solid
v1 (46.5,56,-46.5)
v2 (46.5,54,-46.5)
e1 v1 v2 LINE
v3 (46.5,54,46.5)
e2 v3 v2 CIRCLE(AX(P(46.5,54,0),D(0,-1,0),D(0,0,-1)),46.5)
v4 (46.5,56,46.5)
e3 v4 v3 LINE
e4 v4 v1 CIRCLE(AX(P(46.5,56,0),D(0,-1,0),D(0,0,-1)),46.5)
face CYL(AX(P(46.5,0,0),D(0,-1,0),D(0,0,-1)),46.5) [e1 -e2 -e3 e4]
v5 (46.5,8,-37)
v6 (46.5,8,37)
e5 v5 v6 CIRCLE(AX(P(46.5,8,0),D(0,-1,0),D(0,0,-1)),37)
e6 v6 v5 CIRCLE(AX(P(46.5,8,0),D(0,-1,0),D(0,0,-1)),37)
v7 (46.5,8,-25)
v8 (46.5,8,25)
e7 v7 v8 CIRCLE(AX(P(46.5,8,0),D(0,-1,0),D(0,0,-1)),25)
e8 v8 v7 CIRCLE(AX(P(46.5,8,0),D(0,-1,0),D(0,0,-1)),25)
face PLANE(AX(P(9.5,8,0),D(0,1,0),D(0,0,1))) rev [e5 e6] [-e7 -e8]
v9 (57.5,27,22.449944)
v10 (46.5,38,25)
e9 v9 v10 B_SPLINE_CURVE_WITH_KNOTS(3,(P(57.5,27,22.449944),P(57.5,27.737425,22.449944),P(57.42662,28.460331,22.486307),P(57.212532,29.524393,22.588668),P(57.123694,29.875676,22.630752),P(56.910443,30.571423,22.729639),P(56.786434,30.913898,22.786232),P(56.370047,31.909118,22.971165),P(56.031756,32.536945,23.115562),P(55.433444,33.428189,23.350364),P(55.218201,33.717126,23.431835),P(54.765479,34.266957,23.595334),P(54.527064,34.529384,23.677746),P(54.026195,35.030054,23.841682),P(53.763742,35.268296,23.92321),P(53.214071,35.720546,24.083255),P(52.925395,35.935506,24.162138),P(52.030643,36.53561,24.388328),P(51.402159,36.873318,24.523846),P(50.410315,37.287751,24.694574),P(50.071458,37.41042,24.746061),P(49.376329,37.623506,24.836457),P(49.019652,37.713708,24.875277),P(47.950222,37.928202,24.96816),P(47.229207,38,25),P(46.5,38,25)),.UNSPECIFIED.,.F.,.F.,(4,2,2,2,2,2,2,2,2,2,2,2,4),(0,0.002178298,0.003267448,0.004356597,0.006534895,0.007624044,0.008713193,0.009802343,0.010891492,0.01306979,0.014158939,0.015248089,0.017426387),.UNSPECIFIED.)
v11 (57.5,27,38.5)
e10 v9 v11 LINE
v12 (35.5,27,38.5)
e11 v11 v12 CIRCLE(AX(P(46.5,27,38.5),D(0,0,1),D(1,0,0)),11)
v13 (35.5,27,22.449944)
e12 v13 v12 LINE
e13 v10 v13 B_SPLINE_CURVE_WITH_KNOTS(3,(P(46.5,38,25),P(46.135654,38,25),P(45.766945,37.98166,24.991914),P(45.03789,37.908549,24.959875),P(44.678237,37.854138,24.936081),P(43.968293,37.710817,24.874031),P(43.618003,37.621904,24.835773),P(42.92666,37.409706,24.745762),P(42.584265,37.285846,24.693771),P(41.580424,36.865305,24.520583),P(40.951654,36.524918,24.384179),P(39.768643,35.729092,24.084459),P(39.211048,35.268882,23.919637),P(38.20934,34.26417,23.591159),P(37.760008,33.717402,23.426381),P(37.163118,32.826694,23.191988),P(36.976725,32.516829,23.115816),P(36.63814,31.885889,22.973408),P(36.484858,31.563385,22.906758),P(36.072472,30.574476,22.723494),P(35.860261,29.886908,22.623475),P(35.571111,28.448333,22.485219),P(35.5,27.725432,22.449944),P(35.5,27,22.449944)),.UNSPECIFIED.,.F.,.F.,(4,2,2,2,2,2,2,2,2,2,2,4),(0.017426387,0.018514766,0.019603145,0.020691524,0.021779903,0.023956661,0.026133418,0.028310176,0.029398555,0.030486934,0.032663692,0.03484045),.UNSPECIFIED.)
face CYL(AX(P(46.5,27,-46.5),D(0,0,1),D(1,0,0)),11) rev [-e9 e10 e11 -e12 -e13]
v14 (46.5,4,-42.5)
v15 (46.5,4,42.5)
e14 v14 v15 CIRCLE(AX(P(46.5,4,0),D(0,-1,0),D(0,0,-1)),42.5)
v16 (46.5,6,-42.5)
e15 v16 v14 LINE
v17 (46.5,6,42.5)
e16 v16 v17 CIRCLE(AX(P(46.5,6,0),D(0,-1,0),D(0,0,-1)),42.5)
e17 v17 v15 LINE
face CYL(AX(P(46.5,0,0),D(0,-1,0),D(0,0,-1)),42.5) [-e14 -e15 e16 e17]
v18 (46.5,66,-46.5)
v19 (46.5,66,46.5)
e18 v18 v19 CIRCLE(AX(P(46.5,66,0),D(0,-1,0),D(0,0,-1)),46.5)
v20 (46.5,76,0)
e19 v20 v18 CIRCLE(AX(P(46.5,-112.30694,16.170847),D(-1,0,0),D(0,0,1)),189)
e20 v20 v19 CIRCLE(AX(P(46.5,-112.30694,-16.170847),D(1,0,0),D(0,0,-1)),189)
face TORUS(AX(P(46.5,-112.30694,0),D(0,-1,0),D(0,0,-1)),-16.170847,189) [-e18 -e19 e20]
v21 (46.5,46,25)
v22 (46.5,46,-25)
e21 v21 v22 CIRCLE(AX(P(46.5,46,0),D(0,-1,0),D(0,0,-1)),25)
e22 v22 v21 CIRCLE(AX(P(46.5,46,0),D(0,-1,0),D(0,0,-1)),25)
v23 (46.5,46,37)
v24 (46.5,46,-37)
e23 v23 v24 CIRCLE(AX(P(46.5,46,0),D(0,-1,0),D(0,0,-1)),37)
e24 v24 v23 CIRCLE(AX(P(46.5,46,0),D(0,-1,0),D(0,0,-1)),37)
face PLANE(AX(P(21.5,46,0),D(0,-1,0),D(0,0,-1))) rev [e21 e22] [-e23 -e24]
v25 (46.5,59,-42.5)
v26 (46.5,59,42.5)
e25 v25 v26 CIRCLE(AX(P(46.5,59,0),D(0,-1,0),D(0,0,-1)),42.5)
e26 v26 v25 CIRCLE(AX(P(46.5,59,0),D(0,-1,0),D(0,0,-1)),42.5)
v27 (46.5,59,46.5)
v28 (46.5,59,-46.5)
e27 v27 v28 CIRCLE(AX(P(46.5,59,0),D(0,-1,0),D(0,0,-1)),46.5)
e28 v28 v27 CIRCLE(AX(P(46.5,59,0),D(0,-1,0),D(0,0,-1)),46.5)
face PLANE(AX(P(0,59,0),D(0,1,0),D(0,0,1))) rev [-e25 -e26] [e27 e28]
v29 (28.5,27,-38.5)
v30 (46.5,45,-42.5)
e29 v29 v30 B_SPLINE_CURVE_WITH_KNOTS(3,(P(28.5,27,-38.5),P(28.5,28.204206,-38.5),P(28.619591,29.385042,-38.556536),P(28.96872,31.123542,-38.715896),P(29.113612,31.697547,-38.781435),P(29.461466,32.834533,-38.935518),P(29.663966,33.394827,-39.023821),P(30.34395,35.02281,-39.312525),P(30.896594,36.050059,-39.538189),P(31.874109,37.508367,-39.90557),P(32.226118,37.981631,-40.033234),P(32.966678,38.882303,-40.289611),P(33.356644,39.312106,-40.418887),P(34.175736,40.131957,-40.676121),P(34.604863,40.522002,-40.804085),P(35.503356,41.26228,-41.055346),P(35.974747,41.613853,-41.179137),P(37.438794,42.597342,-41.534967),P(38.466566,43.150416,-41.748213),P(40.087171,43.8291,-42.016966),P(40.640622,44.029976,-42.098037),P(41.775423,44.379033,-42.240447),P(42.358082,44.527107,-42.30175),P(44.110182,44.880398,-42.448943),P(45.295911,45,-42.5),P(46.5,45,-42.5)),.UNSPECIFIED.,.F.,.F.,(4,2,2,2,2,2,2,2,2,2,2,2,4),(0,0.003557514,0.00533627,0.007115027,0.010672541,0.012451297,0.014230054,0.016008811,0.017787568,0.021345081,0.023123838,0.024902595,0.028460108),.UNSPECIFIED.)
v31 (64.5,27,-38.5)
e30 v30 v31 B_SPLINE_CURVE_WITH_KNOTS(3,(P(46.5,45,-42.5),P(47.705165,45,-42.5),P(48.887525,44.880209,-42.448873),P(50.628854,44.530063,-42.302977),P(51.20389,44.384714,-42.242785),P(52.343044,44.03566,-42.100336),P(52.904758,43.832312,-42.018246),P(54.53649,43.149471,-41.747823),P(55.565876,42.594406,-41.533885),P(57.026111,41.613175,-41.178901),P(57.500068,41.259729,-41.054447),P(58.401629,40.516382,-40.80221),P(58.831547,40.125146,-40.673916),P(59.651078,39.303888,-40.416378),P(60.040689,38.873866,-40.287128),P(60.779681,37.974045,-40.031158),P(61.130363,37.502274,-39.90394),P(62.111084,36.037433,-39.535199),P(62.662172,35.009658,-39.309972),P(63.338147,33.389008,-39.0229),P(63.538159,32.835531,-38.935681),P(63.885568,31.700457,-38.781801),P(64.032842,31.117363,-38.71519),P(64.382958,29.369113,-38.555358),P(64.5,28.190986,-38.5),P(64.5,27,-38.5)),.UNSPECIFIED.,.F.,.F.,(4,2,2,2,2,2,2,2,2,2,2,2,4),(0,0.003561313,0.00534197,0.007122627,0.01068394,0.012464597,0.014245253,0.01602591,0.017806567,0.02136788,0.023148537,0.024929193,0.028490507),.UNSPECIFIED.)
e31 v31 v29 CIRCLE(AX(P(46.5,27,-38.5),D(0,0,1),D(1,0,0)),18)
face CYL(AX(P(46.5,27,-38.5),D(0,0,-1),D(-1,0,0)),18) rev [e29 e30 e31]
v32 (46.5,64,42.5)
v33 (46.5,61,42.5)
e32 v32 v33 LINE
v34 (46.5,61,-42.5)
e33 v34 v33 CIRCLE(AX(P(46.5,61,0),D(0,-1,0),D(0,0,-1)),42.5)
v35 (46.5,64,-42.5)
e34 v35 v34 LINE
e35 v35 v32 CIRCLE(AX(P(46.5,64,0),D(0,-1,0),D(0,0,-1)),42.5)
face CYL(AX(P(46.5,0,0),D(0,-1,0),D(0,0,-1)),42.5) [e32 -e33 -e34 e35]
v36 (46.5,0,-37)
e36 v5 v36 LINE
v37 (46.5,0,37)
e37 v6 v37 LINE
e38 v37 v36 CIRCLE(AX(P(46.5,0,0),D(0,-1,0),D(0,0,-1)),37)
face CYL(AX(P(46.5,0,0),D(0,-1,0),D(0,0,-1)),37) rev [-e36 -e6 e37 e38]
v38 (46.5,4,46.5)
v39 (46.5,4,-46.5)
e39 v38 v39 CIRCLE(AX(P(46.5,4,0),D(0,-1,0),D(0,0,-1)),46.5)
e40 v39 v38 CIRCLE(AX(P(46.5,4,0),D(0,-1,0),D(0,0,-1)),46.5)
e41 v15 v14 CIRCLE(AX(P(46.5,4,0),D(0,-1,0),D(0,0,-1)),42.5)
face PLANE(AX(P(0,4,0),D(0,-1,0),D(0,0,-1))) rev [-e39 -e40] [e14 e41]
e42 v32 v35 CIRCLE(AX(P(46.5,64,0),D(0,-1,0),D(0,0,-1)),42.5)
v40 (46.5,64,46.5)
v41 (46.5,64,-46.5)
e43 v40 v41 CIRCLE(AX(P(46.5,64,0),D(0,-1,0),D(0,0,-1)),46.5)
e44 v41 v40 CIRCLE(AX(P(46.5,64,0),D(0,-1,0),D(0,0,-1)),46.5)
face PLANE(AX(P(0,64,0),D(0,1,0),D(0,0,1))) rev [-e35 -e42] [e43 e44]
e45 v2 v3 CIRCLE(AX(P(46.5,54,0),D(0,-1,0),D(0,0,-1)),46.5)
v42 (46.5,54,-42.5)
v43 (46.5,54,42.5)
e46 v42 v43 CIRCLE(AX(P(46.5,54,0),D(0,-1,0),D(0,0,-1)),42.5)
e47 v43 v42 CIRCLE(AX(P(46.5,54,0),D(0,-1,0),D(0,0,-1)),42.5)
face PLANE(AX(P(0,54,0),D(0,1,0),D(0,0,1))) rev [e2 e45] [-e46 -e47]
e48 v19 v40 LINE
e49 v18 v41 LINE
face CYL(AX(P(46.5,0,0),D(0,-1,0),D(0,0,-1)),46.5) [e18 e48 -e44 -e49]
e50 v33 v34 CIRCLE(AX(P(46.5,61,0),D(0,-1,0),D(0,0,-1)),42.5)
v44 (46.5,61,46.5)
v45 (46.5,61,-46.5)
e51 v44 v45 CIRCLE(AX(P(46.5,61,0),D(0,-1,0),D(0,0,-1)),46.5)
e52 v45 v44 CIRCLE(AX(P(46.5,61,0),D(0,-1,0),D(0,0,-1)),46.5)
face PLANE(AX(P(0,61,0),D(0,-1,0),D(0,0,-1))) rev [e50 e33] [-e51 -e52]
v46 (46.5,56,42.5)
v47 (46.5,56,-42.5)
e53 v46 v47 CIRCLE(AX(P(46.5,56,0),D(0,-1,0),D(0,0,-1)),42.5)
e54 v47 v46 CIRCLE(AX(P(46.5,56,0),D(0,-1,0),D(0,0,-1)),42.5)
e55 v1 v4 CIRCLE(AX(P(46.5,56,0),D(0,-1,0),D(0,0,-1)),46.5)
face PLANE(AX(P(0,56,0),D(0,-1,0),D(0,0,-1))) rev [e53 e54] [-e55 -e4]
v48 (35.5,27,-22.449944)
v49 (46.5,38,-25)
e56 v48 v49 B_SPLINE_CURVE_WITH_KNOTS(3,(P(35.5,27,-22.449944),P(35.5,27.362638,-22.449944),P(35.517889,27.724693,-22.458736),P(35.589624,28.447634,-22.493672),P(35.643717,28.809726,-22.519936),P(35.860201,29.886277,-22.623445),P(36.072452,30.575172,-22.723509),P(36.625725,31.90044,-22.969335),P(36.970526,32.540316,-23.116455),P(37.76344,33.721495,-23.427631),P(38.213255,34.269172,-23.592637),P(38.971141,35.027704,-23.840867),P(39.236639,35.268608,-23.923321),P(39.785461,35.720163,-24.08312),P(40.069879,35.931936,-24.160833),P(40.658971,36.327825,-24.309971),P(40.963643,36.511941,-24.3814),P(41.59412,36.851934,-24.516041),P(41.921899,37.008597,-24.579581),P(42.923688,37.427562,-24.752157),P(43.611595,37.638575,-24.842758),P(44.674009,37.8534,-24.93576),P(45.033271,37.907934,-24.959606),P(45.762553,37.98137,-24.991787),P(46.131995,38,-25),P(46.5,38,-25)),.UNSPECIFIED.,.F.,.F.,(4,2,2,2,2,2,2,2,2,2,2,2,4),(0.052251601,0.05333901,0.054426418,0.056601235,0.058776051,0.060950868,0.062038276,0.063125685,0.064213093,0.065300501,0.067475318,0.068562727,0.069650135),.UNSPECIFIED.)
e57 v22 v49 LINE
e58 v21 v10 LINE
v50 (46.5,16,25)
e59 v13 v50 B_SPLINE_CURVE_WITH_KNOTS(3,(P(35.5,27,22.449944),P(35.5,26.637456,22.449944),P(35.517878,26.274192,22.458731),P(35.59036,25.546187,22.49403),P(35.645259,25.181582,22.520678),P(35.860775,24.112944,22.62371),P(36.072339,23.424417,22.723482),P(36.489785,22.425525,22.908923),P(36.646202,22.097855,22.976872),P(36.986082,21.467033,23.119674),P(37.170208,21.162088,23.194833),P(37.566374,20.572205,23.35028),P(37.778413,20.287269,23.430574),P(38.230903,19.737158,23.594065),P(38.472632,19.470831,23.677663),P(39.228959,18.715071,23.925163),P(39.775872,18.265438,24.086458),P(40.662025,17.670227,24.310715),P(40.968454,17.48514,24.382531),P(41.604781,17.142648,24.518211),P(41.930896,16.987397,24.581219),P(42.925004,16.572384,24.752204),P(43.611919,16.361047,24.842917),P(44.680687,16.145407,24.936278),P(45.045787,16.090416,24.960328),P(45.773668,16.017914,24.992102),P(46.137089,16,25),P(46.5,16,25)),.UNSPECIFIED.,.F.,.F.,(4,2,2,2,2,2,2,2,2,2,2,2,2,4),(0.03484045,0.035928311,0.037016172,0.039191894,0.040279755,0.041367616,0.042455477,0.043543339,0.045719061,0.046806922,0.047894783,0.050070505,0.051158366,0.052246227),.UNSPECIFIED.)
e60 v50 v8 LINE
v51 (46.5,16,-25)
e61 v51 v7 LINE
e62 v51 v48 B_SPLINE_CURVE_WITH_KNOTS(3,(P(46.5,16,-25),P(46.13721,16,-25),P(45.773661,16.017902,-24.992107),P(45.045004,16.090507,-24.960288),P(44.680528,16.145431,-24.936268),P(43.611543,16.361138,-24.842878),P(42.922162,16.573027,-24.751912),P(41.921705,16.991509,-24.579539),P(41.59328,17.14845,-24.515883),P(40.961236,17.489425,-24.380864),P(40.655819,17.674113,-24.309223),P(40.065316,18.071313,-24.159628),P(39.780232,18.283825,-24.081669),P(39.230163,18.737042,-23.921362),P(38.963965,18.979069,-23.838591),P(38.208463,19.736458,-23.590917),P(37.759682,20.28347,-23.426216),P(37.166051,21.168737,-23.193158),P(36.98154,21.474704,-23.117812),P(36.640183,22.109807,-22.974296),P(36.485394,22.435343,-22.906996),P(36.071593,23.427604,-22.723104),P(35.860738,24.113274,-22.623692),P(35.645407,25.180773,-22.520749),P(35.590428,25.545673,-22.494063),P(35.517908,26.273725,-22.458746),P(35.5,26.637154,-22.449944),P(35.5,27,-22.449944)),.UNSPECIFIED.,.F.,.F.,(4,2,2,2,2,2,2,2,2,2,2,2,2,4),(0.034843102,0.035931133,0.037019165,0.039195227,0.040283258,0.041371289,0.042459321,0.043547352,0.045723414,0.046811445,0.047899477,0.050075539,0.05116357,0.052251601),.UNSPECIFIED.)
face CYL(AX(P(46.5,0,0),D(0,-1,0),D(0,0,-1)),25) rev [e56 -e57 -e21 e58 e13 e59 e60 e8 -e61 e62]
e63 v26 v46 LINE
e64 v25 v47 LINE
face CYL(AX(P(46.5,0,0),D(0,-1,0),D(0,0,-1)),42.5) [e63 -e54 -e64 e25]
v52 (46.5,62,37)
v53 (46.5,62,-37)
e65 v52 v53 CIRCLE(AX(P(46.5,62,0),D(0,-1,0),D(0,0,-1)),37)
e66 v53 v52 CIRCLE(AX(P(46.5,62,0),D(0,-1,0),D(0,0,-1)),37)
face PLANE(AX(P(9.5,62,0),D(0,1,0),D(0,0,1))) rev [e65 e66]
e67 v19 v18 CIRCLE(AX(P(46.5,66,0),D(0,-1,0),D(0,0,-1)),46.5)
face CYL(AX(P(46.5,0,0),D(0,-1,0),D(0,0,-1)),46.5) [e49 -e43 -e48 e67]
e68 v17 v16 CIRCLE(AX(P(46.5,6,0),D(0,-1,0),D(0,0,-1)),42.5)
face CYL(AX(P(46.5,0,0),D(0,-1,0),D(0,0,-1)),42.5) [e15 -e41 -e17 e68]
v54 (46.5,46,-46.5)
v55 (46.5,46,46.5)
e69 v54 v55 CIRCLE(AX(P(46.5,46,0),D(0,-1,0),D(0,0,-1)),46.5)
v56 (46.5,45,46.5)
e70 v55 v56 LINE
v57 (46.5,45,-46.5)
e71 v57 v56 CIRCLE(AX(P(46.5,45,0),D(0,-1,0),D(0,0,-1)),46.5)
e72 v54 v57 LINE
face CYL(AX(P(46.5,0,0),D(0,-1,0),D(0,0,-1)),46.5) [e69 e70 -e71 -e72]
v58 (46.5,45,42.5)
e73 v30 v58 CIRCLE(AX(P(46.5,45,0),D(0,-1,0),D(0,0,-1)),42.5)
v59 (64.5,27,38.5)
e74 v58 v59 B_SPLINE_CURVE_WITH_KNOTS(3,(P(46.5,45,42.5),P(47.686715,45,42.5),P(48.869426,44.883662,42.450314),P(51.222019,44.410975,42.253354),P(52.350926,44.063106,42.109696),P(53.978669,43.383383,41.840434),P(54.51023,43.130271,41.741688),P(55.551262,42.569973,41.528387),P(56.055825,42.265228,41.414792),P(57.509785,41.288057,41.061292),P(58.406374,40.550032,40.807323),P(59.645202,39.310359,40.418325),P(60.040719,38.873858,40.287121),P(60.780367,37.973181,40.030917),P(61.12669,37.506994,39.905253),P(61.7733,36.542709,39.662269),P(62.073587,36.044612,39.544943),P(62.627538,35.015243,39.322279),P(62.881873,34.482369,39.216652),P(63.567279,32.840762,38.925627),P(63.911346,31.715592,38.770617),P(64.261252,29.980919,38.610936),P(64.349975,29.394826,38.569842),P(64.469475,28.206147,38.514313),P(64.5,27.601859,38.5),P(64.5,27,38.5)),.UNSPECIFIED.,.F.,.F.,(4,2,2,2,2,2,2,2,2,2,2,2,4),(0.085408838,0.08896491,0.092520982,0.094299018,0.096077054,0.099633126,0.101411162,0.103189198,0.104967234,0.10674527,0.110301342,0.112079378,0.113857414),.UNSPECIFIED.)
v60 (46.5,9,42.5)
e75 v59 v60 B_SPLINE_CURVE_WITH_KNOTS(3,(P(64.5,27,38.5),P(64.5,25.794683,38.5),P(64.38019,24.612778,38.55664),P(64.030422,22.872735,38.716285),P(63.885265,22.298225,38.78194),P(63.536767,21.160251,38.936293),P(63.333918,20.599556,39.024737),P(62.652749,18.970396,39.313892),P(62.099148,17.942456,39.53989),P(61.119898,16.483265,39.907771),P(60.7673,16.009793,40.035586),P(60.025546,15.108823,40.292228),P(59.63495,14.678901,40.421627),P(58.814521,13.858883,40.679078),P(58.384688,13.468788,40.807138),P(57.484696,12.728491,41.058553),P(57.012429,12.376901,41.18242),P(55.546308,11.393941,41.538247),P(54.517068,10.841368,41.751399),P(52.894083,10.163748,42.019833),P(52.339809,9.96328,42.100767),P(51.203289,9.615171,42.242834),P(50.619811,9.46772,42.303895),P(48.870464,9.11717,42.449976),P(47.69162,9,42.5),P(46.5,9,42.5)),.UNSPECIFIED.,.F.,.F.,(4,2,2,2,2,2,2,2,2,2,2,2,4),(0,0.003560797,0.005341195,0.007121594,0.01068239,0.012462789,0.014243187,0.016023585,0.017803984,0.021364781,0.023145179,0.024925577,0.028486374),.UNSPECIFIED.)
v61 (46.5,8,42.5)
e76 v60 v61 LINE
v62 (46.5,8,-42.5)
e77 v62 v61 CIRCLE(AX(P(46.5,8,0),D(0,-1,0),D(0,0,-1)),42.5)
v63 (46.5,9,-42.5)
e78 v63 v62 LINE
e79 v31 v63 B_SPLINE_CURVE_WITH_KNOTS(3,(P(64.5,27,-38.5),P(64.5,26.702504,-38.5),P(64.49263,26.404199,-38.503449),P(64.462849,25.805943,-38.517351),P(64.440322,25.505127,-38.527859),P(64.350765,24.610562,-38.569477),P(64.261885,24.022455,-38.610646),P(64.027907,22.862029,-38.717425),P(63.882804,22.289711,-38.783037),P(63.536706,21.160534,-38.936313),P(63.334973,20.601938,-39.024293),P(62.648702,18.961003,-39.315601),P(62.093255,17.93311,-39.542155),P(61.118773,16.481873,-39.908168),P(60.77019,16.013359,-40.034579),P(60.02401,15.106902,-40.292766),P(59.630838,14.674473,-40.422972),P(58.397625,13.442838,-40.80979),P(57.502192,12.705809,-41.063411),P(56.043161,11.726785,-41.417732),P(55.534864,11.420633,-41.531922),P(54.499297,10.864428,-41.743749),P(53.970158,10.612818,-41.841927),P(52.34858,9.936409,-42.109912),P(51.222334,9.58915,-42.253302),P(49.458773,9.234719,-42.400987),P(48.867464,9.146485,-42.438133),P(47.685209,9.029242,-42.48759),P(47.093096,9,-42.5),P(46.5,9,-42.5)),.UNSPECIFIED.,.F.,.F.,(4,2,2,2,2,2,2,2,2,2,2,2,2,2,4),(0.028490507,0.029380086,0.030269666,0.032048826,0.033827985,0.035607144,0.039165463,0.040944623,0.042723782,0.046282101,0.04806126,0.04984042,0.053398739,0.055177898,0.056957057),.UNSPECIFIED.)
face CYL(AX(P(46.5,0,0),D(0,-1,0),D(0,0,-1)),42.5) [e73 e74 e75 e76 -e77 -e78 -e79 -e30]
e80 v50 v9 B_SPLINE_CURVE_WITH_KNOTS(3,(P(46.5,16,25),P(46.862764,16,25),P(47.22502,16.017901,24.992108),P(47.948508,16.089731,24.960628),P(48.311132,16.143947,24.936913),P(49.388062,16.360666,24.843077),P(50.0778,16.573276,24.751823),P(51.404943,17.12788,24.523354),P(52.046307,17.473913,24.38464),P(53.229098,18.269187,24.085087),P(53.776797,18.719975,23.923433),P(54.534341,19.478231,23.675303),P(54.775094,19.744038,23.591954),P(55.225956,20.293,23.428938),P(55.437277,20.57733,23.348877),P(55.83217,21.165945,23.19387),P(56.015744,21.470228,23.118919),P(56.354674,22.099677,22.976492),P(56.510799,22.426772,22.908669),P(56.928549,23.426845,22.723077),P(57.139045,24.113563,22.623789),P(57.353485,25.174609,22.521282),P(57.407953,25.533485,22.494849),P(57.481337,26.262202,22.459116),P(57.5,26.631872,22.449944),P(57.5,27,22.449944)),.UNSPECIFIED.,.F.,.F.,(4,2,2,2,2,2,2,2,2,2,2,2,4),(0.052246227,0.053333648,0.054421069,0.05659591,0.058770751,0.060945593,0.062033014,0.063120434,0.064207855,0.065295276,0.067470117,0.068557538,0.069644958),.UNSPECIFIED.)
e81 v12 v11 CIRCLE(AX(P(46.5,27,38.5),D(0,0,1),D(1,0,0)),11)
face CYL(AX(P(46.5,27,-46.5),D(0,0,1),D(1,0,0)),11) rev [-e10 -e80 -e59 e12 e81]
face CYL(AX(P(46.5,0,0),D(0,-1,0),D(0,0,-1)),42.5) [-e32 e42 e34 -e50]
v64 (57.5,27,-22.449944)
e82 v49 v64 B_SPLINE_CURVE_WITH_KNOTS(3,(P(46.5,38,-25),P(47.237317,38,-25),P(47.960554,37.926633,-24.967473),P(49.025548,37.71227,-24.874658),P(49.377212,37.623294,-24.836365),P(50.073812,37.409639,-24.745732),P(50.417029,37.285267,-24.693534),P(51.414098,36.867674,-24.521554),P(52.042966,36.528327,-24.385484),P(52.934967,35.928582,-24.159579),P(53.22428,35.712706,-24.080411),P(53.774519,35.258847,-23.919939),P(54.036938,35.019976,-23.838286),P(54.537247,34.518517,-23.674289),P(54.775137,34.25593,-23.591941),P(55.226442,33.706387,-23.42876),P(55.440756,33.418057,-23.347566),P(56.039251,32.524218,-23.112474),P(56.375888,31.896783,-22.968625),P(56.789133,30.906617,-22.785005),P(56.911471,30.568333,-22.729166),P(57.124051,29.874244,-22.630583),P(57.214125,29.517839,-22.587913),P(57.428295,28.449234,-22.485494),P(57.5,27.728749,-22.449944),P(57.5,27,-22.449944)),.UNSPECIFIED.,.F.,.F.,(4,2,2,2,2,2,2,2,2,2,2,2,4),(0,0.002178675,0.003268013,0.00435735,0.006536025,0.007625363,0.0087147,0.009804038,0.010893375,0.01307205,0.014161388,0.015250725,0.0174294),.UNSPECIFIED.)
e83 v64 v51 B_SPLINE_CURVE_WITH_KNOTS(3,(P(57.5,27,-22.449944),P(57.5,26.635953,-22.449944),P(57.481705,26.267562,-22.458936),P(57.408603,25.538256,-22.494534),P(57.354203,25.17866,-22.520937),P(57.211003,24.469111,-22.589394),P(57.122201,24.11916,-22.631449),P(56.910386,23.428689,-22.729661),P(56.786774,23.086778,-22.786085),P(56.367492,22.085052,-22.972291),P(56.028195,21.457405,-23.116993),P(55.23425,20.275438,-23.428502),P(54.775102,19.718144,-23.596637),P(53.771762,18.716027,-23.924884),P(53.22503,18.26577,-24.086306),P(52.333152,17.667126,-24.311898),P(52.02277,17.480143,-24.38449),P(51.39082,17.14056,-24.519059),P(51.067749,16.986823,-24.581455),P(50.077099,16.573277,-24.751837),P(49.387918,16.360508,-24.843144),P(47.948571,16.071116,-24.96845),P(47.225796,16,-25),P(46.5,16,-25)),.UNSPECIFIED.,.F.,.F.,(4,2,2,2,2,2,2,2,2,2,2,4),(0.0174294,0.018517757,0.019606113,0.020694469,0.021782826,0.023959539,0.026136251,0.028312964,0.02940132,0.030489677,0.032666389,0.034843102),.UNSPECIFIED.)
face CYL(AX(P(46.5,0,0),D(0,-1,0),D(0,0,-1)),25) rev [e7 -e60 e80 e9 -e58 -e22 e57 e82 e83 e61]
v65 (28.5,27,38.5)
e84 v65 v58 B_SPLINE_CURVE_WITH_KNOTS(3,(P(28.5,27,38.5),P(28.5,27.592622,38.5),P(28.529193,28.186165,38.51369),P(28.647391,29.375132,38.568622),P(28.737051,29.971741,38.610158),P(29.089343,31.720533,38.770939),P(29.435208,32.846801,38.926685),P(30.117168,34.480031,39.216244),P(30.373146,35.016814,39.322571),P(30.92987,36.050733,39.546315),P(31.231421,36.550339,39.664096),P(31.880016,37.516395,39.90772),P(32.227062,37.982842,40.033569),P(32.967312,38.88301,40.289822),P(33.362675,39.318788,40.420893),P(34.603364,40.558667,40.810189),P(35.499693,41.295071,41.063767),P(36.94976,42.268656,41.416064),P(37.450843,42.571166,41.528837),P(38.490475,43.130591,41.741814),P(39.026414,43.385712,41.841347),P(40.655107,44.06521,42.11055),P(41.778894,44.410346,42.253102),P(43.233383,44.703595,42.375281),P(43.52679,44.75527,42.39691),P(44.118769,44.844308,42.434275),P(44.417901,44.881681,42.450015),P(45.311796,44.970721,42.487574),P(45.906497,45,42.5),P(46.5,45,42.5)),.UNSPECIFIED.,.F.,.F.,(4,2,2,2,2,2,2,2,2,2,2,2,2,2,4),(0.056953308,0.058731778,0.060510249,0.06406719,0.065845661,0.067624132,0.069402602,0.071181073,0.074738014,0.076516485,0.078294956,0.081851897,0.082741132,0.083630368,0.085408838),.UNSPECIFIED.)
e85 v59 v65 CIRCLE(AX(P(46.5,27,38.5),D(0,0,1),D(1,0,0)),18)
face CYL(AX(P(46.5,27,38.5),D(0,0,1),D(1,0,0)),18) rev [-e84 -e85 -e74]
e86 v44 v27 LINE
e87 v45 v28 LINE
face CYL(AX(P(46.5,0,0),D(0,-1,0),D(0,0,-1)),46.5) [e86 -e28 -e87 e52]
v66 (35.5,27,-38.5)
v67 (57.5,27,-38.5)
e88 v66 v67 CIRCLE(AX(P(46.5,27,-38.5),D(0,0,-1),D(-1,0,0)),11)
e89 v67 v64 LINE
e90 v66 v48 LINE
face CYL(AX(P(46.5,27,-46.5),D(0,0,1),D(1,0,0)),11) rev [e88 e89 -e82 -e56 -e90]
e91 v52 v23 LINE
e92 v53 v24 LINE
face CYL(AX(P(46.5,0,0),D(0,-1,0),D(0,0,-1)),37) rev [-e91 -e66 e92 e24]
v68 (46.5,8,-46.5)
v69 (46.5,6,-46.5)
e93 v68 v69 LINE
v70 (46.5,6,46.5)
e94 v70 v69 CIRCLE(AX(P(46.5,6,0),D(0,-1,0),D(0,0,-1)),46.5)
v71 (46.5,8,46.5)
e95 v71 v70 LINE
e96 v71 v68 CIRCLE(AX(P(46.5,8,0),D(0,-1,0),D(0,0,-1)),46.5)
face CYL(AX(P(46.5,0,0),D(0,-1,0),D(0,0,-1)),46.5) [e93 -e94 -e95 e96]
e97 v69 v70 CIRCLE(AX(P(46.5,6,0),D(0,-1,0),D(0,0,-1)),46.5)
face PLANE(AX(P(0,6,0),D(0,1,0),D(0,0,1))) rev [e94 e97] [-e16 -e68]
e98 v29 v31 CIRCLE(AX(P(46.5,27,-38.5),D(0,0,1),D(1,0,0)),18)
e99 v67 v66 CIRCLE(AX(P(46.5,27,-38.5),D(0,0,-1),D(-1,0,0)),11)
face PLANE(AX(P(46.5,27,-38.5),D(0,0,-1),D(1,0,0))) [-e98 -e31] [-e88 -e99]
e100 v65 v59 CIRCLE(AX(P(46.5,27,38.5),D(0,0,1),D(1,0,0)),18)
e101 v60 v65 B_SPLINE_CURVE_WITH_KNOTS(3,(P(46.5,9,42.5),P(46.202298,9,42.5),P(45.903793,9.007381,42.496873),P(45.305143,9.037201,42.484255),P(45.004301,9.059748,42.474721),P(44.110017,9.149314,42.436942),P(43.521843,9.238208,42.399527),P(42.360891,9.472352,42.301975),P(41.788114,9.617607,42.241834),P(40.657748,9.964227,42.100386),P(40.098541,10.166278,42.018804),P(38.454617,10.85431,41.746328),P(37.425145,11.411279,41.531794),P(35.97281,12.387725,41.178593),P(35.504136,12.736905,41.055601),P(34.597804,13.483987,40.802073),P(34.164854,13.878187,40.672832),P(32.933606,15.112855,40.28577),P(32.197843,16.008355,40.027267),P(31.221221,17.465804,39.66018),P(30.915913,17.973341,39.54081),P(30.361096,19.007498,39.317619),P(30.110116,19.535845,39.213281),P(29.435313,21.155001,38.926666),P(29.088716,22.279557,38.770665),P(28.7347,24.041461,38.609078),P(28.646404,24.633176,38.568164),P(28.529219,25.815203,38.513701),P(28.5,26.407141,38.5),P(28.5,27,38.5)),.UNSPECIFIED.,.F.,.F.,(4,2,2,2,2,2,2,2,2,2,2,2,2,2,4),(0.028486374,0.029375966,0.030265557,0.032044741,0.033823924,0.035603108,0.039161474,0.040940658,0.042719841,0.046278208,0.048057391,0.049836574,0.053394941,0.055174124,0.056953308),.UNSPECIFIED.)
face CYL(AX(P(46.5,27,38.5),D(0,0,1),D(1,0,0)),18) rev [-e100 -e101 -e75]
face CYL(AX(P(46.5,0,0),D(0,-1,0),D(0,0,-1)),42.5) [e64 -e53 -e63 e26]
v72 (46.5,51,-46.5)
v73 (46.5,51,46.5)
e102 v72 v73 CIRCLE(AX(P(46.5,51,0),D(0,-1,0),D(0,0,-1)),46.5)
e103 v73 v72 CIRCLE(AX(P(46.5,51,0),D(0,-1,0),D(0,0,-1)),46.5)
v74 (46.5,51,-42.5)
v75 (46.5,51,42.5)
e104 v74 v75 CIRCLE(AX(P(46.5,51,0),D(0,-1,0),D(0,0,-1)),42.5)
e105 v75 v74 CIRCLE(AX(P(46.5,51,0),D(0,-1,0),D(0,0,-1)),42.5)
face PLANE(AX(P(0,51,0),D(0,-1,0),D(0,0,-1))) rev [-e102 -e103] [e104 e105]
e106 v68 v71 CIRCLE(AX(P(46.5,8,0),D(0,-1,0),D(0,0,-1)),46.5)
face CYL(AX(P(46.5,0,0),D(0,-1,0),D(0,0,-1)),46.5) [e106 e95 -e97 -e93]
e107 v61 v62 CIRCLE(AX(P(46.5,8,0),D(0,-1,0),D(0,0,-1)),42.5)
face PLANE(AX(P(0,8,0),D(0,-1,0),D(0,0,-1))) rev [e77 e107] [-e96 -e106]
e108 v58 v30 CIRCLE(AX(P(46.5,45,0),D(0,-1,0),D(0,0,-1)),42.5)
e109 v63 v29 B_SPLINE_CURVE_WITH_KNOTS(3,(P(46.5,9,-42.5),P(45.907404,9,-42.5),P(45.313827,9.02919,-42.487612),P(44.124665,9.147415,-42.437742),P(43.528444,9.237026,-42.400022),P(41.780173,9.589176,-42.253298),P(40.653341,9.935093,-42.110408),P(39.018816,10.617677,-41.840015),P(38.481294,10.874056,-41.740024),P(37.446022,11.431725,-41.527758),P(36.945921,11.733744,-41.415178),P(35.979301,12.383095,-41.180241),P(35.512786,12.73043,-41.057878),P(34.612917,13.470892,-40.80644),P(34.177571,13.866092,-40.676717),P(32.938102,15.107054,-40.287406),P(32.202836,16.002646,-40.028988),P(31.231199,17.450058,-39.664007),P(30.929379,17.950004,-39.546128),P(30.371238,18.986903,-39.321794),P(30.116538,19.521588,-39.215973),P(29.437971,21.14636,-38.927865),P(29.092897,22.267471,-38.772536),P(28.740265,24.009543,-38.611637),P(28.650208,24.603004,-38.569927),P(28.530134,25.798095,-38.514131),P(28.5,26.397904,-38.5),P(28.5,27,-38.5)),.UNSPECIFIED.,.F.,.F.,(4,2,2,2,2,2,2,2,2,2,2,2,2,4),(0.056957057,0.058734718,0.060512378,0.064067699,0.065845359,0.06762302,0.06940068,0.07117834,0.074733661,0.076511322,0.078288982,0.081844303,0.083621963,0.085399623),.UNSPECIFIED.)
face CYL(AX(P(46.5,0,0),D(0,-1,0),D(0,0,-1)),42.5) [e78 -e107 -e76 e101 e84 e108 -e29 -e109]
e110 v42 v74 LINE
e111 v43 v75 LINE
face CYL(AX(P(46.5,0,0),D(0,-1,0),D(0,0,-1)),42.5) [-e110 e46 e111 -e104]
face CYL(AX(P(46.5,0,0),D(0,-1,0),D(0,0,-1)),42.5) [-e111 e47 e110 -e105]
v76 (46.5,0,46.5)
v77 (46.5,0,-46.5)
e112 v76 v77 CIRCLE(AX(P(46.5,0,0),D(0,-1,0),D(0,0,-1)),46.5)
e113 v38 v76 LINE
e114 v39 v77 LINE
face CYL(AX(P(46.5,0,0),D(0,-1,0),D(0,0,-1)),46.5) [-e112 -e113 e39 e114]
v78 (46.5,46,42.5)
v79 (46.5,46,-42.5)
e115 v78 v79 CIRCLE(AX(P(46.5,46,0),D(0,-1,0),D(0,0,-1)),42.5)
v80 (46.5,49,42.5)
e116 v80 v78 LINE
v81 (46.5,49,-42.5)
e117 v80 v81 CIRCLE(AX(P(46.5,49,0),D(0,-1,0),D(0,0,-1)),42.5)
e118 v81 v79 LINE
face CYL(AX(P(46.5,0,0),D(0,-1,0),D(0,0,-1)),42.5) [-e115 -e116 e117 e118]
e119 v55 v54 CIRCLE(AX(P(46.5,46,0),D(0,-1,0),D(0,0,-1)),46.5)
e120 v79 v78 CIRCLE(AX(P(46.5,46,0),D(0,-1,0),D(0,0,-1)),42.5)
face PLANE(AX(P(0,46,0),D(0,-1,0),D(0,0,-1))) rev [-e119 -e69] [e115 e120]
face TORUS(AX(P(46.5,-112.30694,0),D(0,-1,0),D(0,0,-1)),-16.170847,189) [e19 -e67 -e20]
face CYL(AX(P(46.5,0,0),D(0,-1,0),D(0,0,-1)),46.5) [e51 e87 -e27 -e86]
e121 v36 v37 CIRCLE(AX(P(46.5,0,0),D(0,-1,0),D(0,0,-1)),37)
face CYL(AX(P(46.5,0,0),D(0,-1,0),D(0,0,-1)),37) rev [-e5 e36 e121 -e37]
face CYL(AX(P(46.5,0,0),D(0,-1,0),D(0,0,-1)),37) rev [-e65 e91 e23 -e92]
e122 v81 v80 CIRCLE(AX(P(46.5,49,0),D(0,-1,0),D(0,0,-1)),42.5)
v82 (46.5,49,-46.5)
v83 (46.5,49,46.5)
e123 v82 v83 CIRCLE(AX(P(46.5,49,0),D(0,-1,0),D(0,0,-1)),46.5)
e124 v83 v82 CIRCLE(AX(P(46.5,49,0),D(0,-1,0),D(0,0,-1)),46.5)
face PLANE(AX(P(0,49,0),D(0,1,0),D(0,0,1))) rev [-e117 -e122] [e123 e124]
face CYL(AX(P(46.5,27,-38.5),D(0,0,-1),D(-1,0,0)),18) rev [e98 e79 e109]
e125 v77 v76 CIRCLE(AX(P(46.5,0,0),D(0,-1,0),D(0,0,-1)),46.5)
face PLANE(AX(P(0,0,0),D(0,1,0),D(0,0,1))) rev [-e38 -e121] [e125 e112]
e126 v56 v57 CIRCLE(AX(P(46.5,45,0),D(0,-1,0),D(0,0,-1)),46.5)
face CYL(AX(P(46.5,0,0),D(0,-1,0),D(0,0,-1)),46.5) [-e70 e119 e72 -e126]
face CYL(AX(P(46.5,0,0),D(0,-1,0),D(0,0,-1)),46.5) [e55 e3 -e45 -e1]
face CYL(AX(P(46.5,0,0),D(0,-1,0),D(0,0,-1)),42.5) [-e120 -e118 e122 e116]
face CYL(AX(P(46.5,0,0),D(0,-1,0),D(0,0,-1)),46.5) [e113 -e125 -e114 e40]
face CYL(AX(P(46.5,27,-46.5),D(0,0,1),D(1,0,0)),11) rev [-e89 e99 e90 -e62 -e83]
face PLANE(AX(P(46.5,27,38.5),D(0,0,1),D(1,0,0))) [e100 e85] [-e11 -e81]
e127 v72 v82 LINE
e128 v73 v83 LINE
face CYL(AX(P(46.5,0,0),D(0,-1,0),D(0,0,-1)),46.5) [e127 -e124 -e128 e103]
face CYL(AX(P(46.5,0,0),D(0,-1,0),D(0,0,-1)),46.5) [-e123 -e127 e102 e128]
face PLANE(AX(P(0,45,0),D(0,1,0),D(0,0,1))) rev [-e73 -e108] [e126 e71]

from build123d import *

# Parameters (mm, degrees)
PIN_BOSS_RECESS_SKETCH_R = 18
PIN_BOSS_RECESS_DEPTH    = 4
PIN_BORE_SKETCH_R        = 11
PIN_BORE_22_DEPTH        = 150.48578545


with BuildPart() as part:
    # Piston Profile Sketch → Piston Body Revolve (revolve)
    with BuildSketch(Plane.XY, mode=Mode.PRIVATE) as piston_body_revolve_sk:
        with BuildLine():
            Line((0, 0), (9.5, 0))
            Line((9.5, 0), (9.5, 8))
            Line((9.5, 8), (21.5, 8))
            Line((21.5, 8), (21.5, 46))
            Line((21.5, 46), (9.5, 46))
            Line((9.5, 46), (9.5, 62))
            Line((9.5, 62), (46.5, 62))
            Line((46.5, 62), (46.5, 76))
            ThreePointArc((46.5, 76), (22.934174039, 72.468590717), (0, 66))
            Line((0, 66), (0, 64))
            Line((0, 64), (4, 64))
            Line((4, 64), (4, 61))
            Line((4, 61), (0, 61))
            Line((0, 61), (0, 59))
            Line((0, 59), (4, 59))
            Line((4, 59), (4, 56))
            Line((4, 56), (0, 56))
            Line((0, 56), (0, 54))
            Line((0, 54), (4, 54))
            Line((4, 54), (4, 51))
            Line((4, 51), (0, 51))
            Line((0, 51), (0, 49))
            Line((0, 49), (4, 49))
            Line((4, 49), (4, 46))
            Line((4, 46), (0, 46))
            Line((0, 46), (0, 45))
            Line((0, 45), (4, 45))
            Line((4, 45), (4, 8))
            Line((4, 8), (0, 8))
            Line((0, 8), (0, 6))
            Line((0, 6), (4, 6))
            Line((4, 6), (4, 4))
            Line((4, 4), (0, 4))
            Line((0, 4), (0, 0))
        make_face()
    revolve(piston_body_revolve_sk.sketch.rotate(Axis((46.5, 0, 0), (0, 1, 0)), 270), axis=Axis((46.5, 0, 0), (0, 1, 0)))

    # Pin Boss Recess Sketch → Pin Boss Recess (cut)
    with BuildSketch(Plane.XY.offset(42.5)):
        with Locations((46.5, 27)):
            Circle(PIN_BOSS_RECESS_SKETCH_R)
    pin_boss_recess = extrude(amount=-PIN_BOSS_RECESS_DEPTH, mode=Mode.SUBTRACT)

    # Pin Boss Recess Mirror: Pin Boss Recess across plane
    add(pin_boss_recess.mirror(Plane.XY), mode=Mode.SUBTRACT)

    # Pin Bore Sketch → Pin Bore Ø22 (cut, through all)
    with BuildSketch(Plane.XY.offset(42.5)):
        with Locations(Location((46.5, 27, 0), (0, 0, 90))):
            Circle(PIN_BORE_SKETCH_R)
    extrude(amount=-PIN_BORE_22_DEPTH, mode=Mode.SUBTRACT)


solid = part.part
